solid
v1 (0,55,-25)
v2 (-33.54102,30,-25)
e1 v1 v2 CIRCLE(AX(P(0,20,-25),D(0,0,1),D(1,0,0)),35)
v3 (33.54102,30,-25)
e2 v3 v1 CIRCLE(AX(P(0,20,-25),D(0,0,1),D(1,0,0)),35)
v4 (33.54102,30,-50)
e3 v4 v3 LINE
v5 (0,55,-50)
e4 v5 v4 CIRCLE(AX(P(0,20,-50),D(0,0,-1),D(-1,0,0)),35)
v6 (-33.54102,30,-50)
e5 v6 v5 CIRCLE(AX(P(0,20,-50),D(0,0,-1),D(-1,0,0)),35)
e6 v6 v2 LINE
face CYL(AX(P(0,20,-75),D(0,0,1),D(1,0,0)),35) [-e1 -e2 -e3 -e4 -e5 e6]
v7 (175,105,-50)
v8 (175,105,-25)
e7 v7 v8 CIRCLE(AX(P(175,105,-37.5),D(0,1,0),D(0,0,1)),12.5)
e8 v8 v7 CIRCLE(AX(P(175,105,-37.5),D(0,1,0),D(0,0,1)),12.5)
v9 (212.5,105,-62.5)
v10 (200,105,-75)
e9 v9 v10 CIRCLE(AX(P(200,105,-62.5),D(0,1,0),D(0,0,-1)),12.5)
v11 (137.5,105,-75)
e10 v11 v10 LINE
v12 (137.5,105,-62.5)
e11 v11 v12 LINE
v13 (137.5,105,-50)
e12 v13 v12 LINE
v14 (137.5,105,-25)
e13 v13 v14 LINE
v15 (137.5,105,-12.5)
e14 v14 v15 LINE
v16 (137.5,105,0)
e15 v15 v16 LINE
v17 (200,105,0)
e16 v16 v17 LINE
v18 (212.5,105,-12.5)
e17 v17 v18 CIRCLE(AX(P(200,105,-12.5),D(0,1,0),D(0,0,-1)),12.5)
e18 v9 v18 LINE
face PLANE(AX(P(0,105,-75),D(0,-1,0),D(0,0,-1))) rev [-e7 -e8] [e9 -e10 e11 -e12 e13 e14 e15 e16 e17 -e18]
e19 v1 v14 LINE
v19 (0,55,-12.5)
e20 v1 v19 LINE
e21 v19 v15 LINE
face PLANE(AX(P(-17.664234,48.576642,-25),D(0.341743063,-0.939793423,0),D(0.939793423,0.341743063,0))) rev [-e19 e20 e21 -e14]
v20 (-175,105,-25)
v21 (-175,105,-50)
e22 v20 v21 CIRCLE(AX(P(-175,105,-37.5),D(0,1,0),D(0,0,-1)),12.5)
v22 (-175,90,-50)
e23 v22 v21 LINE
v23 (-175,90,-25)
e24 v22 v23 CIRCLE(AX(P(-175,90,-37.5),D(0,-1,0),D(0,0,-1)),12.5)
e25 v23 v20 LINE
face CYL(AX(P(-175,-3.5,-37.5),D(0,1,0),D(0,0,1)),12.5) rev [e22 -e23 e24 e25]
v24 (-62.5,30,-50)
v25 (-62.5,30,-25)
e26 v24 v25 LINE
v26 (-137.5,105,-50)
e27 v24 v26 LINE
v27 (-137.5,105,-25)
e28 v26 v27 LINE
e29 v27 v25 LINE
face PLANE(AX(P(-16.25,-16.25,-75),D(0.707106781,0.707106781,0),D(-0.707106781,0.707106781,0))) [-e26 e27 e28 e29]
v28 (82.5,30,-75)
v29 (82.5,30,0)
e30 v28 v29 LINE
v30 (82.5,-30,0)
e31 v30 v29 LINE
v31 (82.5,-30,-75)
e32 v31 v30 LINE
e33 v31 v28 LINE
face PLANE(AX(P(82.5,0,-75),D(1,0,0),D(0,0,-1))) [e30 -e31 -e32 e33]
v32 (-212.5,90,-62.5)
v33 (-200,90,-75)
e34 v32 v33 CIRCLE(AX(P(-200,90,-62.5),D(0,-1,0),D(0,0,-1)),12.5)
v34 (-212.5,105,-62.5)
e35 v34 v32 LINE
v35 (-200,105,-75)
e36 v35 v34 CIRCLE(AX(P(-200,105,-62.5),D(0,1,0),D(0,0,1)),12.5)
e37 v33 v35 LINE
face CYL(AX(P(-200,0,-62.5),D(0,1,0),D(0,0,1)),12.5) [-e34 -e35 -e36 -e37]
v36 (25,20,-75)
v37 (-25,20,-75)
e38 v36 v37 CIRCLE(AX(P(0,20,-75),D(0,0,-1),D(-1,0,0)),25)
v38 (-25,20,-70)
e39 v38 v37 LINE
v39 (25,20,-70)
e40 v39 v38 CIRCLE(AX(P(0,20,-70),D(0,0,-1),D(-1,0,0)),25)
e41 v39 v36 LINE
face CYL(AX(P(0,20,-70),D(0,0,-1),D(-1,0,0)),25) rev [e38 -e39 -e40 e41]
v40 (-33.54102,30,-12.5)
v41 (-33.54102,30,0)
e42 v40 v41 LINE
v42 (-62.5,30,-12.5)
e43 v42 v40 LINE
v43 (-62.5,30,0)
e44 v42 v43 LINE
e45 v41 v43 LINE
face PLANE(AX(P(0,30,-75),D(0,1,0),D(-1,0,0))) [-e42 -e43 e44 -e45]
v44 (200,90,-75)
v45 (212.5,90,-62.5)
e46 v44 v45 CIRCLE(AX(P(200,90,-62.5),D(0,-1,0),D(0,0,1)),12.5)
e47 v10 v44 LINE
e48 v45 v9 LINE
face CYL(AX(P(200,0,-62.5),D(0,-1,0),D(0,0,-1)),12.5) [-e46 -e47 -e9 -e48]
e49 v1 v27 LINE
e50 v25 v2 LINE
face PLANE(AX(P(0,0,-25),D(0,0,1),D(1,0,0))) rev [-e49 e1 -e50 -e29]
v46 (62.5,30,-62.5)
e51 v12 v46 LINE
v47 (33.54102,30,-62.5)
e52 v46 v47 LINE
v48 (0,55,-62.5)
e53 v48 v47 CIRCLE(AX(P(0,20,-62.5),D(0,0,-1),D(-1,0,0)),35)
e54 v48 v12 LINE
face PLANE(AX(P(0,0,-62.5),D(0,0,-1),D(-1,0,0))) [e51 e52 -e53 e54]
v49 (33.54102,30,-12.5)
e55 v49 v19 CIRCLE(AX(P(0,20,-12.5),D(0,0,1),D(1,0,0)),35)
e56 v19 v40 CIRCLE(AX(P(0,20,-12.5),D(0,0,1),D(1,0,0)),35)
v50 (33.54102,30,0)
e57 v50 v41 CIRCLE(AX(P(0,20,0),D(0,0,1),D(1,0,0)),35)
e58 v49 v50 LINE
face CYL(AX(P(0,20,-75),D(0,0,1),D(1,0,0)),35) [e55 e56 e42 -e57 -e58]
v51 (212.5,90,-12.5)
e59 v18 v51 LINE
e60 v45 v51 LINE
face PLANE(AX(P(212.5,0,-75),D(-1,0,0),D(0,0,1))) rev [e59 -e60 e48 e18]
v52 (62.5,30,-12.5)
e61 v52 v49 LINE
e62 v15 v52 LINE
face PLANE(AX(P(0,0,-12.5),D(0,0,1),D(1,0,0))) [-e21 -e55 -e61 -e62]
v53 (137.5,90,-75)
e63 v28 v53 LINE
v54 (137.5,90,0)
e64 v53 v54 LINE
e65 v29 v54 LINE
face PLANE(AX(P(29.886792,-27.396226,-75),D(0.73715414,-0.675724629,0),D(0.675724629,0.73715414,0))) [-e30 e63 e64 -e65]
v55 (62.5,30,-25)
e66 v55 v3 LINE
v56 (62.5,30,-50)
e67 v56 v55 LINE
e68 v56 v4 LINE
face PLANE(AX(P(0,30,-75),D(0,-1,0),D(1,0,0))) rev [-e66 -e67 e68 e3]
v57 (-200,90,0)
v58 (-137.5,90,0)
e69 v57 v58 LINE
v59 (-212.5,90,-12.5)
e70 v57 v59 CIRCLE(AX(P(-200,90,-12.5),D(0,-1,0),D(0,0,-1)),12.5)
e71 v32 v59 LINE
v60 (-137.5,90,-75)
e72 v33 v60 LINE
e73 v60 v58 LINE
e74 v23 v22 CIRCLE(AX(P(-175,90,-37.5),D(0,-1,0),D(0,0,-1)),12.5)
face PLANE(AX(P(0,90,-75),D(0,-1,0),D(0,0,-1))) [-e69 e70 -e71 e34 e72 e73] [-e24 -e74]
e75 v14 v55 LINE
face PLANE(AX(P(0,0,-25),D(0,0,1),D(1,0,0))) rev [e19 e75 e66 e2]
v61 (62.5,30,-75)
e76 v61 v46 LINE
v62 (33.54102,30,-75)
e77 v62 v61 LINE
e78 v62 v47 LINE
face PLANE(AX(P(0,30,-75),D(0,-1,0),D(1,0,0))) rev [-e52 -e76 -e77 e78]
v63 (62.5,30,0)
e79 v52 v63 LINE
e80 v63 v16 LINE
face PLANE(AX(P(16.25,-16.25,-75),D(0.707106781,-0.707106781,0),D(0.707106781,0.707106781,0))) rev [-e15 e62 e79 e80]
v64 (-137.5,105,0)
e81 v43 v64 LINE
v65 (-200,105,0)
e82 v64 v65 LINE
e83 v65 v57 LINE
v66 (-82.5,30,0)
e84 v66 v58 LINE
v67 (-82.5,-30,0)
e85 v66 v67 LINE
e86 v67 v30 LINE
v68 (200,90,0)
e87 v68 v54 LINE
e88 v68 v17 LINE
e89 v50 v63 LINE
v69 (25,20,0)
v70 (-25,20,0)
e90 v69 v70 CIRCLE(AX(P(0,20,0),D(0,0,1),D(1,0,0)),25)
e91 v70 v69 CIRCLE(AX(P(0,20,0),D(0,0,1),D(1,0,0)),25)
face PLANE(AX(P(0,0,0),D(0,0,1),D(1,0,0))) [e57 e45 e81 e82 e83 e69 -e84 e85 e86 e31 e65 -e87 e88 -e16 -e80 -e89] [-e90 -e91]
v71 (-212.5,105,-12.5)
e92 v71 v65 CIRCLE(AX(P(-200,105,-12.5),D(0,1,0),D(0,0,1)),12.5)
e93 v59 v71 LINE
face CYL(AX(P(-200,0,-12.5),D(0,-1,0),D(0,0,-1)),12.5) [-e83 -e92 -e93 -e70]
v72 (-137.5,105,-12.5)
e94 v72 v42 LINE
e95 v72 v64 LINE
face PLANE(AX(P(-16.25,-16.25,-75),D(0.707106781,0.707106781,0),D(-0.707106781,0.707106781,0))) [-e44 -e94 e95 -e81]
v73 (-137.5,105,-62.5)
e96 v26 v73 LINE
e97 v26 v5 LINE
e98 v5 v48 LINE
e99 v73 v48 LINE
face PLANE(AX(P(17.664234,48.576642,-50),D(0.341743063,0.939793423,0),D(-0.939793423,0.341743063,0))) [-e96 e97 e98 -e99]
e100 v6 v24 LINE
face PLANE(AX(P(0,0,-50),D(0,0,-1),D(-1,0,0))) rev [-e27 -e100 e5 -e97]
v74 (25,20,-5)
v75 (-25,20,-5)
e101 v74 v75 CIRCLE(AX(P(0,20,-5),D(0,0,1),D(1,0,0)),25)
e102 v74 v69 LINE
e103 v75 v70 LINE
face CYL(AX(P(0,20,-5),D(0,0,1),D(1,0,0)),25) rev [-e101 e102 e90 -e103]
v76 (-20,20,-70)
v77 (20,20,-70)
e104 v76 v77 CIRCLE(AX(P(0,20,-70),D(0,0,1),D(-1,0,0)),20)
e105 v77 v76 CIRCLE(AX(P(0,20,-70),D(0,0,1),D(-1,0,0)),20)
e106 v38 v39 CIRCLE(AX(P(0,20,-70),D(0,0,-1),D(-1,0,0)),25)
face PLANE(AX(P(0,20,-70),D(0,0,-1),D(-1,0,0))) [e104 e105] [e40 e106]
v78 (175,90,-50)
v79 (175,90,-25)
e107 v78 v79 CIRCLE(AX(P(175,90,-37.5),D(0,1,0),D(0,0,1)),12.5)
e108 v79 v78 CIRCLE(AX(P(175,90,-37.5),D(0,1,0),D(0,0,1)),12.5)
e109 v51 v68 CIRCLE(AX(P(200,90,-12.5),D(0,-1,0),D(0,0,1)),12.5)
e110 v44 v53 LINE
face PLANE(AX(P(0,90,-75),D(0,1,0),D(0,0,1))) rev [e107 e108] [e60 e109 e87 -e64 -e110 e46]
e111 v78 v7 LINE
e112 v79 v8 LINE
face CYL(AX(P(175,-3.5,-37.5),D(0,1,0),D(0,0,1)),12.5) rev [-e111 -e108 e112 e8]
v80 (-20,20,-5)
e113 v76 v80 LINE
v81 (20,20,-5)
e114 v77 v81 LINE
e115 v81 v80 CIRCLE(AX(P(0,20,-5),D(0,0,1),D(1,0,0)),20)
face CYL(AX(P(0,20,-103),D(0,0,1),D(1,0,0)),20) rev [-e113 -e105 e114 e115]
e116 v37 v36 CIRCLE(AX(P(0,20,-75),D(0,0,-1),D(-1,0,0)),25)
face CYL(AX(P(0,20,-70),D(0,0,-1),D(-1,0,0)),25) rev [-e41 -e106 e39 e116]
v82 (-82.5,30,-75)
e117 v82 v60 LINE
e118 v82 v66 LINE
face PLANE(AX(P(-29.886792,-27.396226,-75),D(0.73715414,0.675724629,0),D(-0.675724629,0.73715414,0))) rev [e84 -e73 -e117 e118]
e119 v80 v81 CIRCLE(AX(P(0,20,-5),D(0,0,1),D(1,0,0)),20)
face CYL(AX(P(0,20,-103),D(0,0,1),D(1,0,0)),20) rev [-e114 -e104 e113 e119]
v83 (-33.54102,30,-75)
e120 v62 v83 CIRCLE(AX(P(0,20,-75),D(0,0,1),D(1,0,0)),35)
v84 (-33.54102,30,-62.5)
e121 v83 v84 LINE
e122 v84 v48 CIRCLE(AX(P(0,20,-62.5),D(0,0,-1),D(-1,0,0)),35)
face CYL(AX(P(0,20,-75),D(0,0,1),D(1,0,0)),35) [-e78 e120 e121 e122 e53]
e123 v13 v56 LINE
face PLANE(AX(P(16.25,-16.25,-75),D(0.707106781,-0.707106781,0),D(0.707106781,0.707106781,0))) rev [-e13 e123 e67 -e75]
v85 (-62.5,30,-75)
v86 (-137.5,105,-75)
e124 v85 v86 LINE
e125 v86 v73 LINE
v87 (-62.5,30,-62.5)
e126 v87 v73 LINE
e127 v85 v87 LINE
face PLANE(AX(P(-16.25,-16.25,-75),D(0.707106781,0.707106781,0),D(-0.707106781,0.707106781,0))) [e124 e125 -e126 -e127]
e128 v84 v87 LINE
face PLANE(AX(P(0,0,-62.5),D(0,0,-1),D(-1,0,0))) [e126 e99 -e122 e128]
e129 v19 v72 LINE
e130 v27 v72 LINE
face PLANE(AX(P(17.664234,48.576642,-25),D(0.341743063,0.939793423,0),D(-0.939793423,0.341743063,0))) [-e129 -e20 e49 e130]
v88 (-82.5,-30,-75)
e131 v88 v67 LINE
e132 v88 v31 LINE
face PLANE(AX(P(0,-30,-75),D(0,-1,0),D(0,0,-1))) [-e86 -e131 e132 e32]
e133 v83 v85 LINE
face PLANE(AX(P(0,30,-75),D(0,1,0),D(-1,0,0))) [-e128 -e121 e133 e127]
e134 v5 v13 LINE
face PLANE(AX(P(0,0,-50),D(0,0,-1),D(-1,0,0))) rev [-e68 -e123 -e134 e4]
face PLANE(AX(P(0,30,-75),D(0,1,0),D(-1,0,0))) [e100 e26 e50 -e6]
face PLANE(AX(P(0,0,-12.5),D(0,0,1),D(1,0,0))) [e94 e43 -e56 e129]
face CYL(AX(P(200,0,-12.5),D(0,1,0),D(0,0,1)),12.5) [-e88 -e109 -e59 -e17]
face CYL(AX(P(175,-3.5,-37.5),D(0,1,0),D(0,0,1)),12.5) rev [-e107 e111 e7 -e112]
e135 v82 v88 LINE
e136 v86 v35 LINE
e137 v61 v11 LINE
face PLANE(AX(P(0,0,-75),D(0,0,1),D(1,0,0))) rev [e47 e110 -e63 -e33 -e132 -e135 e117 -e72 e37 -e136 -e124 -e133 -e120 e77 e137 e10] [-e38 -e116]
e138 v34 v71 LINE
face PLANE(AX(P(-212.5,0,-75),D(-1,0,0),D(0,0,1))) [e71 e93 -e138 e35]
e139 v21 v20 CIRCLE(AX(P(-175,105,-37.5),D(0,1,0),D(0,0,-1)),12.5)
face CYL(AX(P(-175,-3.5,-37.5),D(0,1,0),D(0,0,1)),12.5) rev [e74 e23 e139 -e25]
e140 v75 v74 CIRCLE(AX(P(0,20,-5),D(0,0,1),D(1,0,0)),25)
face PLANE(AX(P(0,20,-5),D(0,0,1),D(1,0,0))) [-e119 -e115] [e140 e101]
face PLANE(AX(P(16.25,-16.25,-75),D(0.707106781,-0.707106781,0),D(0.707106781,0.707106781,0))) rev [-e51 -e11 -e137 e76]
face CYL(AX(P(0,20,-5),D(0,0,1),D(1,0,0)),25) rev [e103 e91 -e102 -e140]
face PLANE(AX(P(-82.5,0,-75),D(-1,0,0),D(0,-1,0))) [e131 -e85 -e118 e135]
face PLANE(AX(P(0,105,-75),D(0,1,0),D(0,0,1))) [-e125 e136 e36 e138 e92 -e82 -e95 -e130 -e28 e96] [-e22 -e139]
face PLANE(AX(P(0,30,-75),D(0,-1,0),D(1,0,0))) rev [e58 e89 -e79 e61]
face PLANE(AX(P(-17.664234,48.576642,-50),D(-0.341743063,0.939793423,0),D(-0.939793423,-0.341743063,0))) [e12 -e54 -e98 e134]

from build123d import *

# Parameters (mm, degrees)
SUPPORT_BODY_DEPTH           = 75
RIB_FRONT_DEPTH              = 12.5
RIB_START                    = -12.5
RIB_BACK_DEPTH               = 12.5
MOUNTING_HOLES_SKETCH_R      = 12.5
MOUNTING_HOLES_2X_25_DEPTH   = 108.5
FLANGE_FILLET_R12_5_A_R      = 12.5
FLANGE_FILLET_R12_5_B_R      = 12.5
FLANGE_FILLET_R12_5_C_R      = 12.5
FLANGE_FILLET_R12_5_D_R      = 12.5
COUNTERBORE_FRONT_SKETCH_R   = 25
COUNTERBORE_FRONT_50X5_DEPTH = 5
SHAFT_BORE_SKETCH_R          = 20
SHAFT_BORE_40_DEPTH          = 98
COUNTERBORE_START            = -5
COUNTERBORE_BACK_SKETCH_R    = 25
COUNTERBORE_BACK_50X5_DEPTH  = 5


with BuildPart() as part:
    # Support Profile Sketch → Support Body (new body)
    with BuildSketch(Plane.XY):
        with BuildLine():
            Line((33.541019662, 30), (62.5, 30))
            Line((62.5, 30), (137.5, 105))
            Line((137.5, 105), (212.5, 105))
            Line((212.5, 105), (212.5, 90))
            Line((212.5, 90), (137.5, 90))
            Line((137.5, 90), (82.5, 30))
            Line((82.5, 30), (82.5, 0))
            Line((82.5, 0), (82.5, -30))
            Line((82.5, -30), (-82.5, -30))
            Line((-82.5, -30), (-82.5, 30))
            Line((-82.5, 30), (-137.5, 90))
            Line((-137.5, 90), (-212.5, 90))
            Line((-212.5, 90), (-212.5, 105))
            Line((-212.5, 105), (-137.5, 105))
            Line((-137.5, 105), (-62.5, 30))
            Line((-62.5, 30), (-33.541019662, 30))
            ThreePointArc((-33.541019662, 30), (0, 55), (33.541019662, 30))
        make_face()
    extrude(amount=-SUPPORT_BODY_DEPTH)

    # Rib Front Sketch → Rib Front (add)
    with BuildSketch(Plane.XY.offset(-12.5)):
        with BuildLine():
            Line((137.5, 105), (0, 55))
            ThreePointArc((0, 55), (20.916500663, 48.062430401), (33.541019662, 30))
            Line((33.541019662, 30), (62.5, 30))
            Line((62.5, 30), (137.5, 105))
        make_face()
        with BuildLine():
            ThreePointArc((-33.541019662, 30), (-20.916500663, 48.062430401), (0, 55))
            Line((0, 55), (-137.5, 105))
            Line((-137.5, 105), (-62.5, 30))
            Line((-62.5, 30), (-33.541019662, 30))
        make_face()
    extrude(amount=-RIB_FRONT_DEPTH)

    # Rib Back Sketch → Rib Back (add)
    with BuildSketch(Plane(origin=(0, 0, -62.5), x_dir=(-1, 0, 0), z_dir=(0, 0, -1)).offset(RIB_START)):
        with BuildLine():
            Line((137.5, 105), (0, 55))
            ThreePointArc((0, 55), (20.916500663, 48.062430401), (33.541019662, 30))
            Line((33.541019662, 30), (62.5, 30))
            Line((62.5, 30), (137.5, 105))
        make_face()
        with BuildLine():
            Line((0, 55), (-137.5, 105))
            Line((-137.5, 105), (-62.5, 30))
            Line((-62.5, 30), (-33.541019662, 30))
            ThreePointArc((-33.541019662, 30), (-20.916500663, 48.062430401), (0, 55))
        make_face()
    extrude(amount=RIB_BACK_DEPTH)

    # Mounting Holes Sketch → Mounting Holes 2xØ25 (cut)
    with BuildSketch(Plane(origin=(0, 105, 0), x_dir=(1, 0, 0), z_dir=(0, 1, 0))):
        with Locations(Location((175, 37.5, 0), (0, 0, 270))):
            Circle(MOUNTING_HOLES_SKETCH_R)
        with Locations(Location((-175, 37.5, 0), (0, 0, 90))):
            Circle(MOUNTING_HOLES_SKETCH_R)
    extrude(amount=-MOUNTING_HOLES_2X_25_DEPTH, mode=Mode.SUBTRACT)

    # Flange Fillet R12.5 A
    flange_fillet_r12_5_a_edges = [part.edges().sort_by_distance(p)[0] for p in [
        (212.5, 97.5, 0),
    ]]
    fillet(flange_fillet_r12_5_a_edges, radius=FLANGE_FILLET_R12_5_A_R)

    # Flange Fillet R12.5 B
    flange_fillet_r12_5_b_edges = [part.edges().sort_by_distance(p)[0] for p in [
        (212.5, 97.5, -75),
    ]]
    fillet(flange_fillet_r12_5_b_edges, radius=FLANGE_FILLET_R12_5_B_R)

    # Flange Fillet R12.5 C
    flange_fillet_r12_5_c_edges = [part.edges().sort_by_distance(p)[0] for p in [
        (-212.5, 97.5, -75),
    ]]
    fillet(flange_fillet_r12_5_c_edges, radius=FLANGE_FILLET_R12_5_C_R)

    # Flange Fillet R12.5 D
    flange_fillet_r12_5_d_edges = [part.edges().sort_by_distance(p)[0] for p in [
        (-212.5, 97.5, 0),
    ]]
    fillet(flange_fillet_r12_5_d_edges, radius=FLANGE_FILLET_R12_5_D_R)

    # Counterbore Front Sketch → Counterbore Front Ø50x5 (cut)
    with BuildSketch(Plane.XY):
        with Locations((0, 20)):
            Circle(COUNTERBORE_FRONT_SKETCH_R)
    extrude(amount=-COUNTERBORE_FRONT_50X5_DEPTH, mode=Mode.SUBTRACT)

    # Shaft Bore Sketch → Shaft Bore Ø40 (cut)
    with BuildSketch(Plane.XY.offset(-5)):
        with Locations((0, 20)):
            Circle(SHAFT_BORE_SKETCH_R)
    extrude(amount=-SHAFT_BORE_40_DEPTH, mode=Mode.SUBTRACT)

    # Counterbore Back Sketch → Counterbore Back Ø50x5 (cut)
    with BuildSketch(Plane(origin=(0, 0, -75), x_dir=(-1, 0, 0), z_dir=(0, 0, -1)).offset(COUNTERBORE_START)):
        with Locations(Location((0, 20, 0), (0, 0, 180))):
            Circle(COUNTERBORE_BACK_SKETCH_R)
    extrude(amount=COUNTERBORE_BACK_50X5_DEPTH, mode=Mode.SUBTRACT)


solid = part.part
